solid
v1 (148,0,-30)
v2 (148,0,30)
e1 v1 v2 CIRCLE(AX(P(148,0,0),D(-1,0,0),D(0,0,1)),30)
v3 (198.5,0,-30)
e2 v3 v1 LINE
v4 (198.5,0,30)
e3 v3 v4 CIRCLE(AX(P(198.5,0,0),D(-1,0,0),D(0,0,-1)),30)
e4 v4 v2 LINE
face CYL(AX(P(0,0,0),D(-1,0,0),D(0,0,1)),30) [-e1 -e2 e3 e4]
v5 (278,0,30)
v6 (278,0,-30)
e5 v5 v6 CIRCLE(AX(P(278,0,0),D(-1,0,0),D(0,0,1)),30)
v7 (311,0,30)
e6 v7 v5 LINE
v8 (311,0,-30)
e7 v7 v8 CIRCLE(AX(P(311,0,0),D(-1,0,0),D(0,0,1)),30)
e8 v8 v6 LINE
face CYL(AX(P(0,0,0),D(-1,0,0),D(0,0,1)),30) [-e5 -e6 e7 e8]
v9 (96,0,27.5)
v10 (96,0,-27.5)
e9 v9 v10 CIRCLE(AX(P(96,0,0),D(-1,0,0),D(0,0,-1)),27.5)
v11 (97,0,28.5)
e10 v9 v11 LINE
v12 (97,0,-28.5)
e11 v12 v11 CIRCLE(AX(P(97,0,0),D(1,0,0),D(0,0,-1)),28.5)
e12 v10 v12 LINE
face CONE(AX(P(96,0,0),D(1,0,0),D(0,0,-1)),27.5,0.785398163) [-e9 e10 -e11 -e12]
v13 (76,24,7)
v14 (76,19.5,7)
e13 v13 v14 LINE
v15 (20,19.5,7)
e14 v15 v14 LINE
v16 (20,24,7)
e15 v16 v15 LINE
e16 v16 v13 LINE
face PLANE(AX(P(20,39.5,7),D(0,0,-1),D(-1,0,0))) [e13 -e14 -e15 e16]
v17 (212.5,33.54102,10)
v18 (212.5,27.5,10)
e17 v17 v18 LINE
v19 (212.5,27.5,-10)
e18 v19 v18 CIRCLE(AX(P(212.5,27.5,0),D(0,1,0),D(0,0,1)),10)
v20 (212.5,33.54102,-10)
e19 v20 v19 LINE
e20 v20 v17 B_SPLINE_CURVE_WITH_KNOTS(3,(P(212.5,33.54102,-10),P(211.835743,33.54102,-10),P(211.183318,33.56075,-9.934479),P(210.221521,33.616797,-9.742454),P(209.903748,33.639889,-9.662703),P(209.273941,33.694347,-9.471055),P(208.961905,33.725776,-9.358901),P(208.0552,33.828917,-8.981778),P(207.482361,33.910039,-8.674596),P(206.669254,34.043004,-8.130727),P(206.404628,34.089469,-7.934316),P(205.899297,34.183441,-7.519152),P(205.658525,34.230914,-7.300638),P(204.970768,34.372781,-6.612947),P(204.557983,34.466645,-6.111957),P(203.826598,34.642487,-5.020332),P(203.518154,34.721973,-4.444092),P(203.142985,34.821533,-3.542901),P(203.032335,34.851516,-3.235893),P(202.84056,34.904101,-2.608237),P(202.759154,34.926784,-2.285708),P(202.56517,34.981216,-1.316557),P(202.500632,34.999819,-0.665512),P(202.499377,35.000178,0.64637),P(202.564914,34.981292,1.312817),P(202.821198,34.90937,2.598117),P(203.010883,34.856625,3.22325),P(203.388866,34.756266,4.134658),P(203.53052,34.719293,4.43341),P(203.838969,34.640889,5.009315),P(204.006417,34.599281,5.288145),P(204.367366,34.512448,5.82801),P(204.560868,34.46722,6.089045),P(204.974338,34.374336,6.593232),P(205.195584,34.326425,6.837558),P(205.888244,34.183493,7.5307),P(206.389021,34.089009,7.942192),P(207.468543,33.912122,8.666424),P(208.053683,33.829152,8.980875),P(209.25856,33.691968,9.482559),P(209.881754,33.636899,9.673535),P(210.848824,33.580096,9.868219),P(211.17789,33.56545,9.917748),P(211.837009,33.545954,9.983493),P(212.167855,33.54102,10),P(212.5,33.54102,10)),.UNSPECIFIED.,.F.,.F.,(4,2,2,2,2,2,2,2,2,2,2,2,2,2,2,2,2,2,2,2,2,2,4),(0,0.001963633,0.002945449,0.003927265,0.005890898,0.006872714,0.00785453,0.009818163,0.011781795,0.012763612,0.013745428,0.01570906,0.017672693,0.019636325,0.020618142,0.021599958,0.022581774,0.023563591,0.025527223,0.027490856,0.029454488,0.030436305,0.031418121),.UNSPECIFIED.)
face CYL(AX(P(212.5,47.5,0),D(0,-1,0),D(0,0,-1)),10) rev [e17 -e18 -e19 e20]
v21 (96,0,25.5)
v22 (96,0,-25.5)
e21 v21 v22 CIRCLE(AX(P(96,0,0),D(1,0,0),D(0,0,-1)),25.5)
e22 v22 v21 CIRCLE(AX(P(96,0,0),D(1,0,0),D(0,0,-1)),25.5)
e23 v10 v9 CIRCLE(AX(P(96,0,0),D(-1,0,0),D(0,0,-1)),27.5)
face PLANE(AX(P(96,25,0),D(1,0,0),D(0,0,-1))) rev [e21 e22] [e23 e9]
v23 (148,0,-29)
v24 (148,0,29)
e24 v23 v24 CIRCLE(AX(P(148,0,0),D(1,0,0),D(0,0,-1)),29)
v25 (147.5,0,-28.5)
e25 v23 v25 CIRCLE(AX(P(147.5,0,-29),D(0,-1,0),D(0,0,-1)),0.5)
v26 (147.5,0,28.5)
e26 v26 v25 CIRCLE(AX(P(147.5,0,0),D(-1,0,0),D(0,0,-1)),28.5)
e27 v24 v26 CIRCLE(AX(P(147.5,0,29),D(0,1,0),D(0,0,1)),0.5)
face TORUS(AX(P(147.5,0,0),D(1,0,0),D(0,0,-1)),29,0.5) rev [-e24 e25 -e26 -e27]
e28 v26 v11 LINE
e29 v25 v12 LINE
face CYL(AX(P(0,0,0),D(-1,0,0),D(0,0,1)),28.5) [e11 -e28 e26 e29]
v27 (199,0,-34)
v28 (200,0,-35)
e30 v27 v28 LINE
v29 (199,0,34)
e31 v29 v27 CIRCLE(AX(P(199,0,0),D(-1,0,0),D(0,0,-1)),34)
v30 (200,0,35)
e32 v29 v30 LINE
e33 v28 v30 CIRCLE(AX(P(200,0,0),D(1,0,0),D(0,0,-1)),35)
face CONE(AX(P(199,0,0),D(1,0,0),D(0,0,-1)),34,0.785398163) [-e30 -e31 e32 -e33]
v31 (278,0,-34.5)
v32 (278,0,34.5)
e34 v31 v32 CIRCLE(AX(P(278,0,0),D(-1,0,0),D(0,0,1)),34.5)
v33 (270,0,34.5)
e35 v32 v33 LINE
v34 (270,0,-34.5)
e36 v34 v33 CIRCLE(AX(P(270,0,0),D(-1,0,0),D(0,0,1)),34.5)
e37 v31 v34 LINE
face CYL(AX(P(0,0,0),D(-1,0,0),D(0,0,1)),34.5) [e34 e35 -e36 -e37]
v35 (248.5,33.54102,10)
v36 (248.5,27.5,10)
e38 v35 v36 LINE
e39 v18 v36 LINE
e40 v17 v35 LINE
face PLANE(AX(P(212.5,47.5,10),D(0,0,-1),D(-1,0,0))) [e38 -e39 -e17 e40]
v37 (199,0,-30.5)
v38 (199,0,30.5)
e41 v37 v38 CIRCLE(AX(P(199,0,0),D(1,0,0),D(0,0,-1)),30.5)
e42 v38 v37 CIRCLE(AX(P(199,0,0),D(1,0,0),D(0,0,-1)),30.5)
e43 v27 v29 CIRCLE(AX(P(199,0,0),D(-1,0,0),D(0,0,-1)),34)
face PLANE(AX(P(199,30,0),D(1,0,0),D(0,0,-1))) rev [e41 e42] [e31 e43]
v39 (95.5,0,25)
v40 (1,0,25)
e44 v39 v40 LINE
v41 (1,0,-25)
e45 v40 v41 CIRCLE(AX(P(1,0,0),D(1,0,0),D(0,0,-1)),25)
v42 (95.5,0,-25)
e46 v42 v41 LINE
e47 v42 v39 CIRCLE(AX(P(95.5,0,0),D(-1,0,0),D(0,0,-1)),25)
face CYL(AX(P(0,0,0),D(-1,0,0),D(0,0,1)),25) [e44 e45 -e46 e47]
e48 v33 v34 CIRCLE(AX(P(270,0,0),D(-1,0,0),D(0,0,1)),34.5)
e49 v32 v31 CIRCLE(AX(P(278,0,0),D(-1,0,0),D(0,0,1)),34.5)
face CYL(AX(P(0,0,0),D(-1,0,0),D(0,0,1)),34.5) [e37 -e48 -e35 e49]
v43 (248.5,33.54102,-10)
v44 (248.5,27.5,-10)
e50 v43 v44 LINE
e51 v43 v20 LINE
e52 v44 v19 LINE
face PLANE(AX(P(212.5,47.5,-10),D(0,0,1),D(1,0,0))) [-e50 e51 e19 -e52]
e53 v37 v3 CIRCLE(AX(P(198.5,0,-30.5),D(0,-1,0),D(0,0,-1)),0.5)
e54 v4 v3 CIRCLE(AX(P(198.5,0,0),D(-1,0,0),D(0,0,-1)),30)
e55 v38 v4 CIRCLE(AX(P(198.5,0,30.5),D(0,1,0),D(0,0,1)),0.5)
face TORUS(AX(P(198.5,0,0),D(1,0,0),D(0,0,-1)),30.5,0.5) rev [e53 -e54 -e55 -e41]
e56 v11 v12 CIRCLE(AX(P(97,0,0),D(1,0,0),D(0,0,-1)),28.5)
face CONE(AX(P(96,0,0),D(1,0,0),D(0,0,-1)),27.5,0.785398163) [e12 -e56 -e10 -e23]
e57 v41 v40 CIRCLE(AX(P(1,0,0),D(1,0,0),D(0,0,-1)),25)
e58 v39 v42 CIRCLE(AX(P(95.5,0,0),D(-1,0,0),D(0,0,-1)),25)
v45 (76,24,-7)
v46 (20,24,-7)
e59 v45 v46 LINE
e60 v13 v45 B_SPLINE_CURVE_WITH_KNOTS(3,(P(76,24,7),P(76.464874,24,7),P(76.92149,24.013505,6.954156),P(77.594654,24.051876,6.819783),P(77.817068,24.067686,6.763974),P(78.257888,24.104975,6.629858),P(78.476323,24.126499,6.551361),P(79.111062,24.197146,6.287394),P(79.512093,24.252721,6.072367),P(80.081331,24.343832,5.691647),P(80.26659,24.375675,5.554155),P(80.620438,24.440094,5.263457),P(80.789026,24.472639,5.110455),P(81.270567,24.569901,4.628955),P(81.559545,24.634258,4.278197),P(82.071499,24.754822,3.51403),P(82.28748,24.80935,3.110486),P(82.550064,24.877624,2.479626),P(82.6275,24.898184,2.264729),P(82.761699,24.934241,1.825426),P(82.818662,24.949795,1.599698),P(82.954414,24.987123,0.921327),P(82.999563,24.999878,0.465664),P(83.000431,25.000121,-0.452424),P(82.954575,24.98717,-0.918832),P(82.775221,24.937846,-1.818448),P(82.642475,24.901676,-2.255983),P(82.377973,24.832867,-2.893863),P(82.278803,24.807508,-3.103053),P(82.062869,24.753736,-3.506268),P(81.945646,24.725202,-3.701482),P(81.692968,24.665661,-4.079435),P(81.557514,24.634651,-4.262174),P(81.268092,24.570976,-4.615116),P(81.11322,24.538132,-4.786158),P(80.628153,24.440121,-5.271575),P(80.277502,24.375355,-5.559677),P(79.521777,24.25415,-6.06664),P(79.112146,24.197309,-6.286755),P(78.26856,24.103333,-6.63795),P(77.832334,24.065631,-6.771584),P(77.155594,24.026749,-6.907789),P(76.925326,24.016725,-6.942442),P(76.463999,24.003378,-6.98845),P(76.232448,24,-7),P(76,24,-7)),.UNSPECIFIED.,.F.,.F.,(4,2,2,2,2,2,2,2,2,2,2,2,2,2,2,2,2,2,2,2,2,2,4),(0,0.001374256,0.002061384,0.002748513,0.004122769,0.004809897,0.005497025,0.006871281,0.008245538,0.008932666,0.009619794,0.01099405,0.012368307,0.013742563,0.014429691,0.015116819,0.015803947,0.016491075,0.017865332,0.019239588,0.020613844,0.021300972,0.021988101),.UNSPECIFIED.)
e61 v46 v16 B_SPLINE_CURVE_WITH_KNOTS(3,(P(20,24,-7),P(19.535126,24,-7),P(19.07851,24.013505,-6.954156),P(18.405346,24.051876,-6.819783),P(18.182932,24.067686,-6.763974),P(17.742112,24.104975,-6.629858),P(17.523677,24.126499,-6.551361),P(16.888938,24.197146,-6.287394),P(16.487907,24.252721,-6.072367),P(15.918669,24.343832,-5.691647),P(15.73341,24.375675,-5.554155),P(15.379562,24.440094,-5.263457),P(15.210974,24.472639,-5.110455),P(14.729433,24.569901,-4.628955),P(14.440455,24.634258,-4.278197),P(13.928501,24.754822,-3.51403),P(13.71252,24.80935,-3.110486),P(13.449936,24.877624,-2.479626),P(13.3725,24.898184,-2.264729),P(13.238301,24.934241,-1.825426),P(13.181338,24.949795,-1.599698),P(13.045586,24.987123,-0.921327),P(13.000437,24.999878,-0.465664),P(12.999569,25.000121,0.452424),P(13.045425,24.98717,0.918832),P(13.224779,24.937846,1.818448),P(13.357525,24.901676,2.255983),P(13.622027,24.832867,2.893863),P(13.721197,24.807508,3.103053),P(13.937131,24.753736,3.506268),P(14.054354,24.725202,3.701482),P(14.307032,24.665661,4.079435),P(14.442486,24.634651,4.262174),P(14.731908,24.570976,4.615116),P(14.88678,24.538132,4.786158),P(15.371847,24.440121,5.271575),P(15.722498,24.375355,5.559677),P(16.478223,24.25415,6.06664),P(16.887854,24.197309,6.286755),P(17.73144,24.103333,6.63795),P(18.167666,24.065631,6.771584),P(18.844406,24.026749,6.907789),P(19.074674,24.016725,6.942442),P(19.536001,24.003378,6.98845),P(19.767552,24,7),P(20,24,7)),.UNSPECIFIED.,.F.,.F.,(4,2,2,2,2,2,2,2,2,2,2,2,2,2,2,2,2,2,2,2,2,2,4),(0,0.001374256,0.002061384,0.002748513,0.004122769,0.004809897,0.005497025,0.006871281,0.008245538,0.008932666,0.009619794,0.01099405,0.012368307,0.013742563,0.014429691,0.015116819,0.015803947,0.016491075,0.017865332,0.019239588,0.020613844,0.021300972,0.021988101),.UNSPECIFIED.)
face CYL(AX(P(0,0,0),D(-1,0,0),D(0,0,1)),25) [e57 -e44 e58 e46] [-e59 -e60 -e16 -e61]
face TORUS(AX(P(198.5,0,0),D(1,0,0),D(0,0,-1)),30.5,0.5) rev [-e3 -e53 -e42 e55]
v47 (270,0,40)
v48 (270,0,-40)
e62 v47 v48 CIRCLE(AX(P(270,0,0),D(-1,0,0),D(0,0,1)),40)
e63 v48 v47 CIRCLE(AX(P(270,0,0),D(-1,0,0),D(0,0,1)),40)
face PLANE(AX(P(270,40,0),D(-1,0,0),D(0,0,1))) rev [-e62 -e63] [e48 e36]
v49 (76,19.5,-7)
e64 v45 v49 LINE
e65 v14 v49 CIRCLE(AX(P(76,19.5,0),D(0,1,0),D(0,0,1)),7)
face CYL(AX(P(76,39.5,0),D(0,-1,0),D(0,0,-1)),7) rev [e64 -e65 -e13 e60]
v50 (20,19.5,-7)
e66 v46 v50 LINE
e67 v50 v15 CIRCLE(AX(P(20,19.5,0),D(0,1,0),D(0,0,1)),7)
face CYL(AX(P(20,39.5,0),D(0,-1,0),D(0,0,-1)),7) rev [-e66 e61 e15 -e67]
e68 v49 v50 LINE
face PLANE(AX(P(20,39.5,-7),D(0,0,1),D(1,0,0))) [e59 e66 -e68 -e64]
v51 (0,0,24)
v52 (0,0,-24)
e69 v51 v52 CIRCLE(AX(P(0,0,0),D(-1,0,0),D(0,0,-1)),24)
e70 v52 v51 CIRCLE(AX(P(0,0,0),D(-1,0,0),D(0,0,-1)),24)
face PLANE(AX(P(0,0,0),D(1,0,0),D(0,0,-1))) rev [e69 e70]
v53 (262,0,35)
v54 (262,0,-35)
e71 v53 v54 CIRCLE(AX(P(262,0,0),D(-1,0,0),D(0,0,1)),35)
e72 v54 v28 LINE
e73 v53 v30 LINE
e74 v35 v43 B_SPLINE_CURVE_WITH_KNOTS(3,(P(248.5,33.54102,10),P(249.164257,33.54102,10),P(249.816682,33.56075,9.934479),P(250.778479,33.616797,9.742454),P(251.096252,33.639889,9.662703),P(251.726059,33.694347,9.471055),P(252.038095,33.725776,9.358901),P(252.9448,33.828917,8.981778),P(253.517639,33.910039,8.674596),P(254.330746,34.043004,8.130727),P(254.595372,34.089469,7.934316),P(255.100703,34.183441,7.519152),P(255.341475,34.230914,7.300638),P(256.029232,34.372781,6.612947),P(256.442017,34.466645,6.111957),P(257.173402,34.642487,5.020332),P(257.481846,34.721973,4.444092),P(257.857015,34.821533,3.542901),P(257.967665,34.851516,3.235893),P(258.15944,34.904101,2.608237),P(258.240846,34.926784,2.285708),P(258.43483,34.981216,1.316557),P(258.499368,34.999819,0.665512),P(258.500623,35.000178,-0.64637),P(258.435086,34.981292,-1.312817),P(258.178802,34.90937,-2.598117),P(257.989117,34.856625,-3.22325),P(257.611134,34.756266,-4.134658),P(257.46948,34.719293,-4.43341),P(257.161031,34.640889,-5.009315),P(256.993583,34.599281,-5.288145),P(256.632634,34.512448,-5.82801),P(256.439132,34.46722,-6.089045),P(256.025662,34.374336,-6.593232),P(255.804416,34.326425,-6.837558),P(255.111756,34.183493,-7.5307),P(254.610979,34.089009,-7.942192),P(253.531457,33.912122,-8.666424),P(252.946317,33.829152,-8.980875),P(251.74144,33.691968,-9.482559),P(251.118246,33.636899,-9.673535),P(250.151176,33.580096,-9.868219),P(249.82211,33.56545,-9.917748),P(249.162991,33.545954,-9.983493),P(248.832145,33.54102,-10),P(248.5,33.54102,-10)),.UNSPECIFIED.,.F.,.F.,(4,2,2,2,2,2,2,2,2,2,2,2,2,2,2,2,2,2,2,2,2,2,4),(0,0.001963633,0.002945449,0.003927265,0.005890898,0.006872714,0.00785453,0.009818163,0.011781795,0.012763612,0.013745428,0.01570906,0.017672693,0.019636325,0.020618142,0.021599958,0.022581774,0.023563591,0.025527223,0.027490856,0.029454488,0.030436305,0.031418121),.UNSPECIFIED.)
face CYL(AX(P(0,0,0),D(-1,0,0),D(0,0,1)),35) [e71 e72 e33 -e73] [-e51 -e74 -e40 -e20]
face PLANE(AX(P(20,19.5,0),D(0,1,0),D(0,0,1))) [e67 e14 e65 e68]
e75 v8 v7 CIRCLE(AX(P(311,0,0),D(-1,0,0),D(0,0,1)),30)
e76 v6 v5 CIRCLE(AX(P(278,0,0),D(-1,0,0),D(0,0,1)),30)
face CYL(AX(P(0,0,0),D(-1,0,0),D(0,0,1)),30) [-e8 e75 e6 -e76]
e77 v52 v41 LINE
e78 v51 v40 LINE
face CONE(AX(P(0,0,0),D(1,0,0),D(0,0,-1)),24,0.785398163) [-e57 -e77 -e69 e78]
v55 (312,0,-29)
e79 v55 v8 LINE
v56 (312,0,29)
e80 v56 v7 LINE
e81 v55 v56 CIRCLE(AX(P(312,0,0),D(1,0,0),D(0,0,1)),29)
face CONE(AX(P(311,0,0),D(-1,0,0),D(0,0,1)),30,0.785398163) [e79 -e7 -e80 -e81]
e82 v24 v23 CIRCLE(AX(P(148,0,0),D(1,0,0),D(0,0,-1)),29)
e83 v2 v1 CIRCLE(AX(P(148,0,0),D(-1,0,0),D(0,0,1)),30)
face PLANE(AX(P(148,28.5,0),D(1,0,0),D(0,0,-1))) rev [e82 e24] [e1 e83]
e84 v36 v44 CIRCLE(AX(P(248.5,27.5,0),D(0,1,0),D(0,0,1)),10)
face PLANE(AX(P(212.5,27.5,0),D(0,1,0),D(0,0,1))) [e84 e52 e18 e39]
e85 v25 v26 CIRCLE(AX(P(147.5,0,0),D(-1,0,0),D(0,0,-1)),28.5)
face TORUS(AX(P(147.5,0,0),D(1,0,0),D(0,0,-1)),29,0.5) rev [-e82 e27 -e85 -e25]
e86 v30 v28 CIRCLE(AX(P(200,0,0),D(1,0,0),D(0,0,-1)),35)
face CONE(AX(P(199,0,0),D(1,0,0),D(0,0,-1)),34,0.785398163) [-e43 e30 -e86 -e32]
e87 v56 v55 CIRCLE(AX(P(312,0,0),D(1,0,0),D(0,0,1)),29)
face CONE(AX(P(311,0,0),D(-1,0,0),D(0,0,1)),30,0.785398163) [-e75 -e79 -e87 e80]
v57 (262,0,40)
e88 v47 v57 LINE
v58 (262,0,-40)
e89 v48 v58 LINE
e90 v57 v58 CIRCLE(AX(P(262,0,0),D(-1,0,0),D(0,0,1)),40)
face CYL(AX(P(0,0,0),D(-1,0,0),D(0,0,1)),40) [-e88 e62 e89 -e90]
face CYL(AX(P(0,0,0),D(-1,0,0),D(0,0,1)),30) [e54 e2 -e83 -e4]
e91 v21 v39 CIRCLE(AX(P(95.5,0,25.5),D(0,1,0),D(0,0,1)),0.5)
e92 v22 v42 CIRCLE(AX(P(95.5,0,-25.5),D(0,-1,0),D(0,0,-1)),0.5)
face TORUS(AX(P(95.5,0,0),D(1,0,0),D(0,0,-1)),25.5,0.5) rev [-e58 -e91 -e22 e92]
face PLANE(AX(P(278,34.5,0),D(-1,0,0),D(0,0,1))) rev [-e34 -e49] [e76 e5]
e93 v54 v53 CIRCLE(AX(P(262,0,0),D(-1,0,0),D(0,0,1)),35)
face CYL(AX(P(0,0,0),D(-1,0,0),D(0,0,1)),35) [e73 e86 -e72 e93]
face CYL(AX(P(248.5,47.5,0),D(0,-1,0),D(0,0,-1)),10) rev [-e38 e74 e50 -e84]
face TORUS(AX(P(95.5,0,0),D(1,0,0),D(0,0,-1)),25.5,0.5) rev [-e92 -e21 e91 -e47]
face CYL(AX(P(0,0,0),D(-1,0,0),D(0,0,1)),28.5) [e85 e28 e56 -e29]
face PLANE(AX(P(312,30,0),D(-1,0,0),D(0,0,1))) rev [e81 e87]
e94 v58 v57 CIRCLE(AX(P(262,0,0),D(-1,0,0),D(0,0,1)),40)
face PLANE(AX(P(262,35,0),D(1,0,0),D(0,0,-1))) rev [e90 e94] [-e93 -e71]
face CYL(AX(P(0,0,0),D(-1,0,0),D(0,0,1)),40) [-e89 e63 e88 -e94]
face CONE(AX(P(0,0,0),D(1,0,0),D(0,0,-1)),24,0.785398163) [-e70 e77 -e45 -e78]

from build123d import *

# Parameters (mm, degrees)
CHAMFER1_SIZE      = 1
CHAMFER2_SIZE      = 1
FILLET1_R          = 0.5
CHAMFER3_SIZE      = 1
CHAMFER4_SIZE      = 1
FILLET2_R          = 0.5
CUT_EXTRUDE1_START = 19.5
CUT_EXTRUDE1_DEPTH = 20
CUT_EXTRUDE2_START = 27.5
CUT_EXTRUDE2_DEPTH = 20


with BuildPart() as part:
    # Sketch1 → Revolve3 (revolve)
    with BuildSketch(Plane.XY, mode=Mode.PRIVATE) as revolve3_sk:
        Polygon((0, 0), (0, 25), (96, 25), (96, 28.5), (148, 28.5), (148, 30), (199, 30), (199, 35), (262, 35), (262, 40), (270, 40), (270, 34.5), (278, 34.5), (278, 30), (312, 30), (312, 0), align=None)
    revolve(revolve3_sk.sketch.rotate(Axis((0, 0, 0), (1, 0, 0)), 90), axis=Axis((0, 0, 0), (1, 0, 0)))

    # Chamfer1
    chamfer1_edges = [part.edges().sort_by_distance(p)[0] for p in [
        (0, 0, -25),
    ]]
    chamfer(chamfer1_edges, length=CHAMFER1_SIZE)

    # Chamfer2
    chamfer2_edges = [part.edges().sort_by_distance(p)[0] for p in [
        (312, 0, -30),
    ]]
    chamfer(chamfer2_edges, length=CHAMFER2_SIZE)

    # Fillet1
    fillet1_edges = [part.edges().sort_by_distance(p)[0] for p in [
        (148, 0, -28.5),
        (96, 0, -25),
    ]]
    fillet(fillet1_edges, radius=FILLET1_R)

    # Chamfer3
    chamfer3_edges = [part.edges().sort_by_distance(p)[0] for p in [
        (199, 0, -35),
    ]]
    chamfer(chamfer3_edges, length=CHAMFER3_SIZE)

    # Chamfer4
    chamfer4_edges = [part.edges().sort_by_distance(p)[0] for p in [
        (96, 0, -28.5),
    ]]
    chamfer(chamfer4_edges, length=CHAMFER4_SIZE)

    # Fillet2
    fillet2_edges = [part.edges().sort_by_distance(p)[0] for p in [
        (199, 0, -30),
    ]]
    fillet(fillet2_edges, radius=FILLET2_R)

    # Sketch2 → Cut-Extrude1 (cut)
    with BuildSketch(Plane(origin=(0, 0, 0), x_dir=(1, 0, 0), z_dir=(0, 1, 0)).offset(CUT_EXTRUDE1_START)):
        with BuildLine():
            Line((20, 7), (76, 7))
            ThreePointArc((76, 7), (83, 0), (76, -7))
            Line((76, -7), (20, -7))
            ThreePointArc((20, -7), (13, 0), (20, 7))
        make_face()
    extrude(amount=CUT_EXTRUDE1_DEPTH, mode=Mode.SUBTRACT)

    # Sketch3 → Cut-Extrude2 (cut)
    with BuildSketch(Plane(origin=(0, 0, 0), x_dir=(1, 0, 0), z_dir=(0, 1, 0)).offset(CUT_EXTRUDE2_START)):
        with BuildLine():
            Line((212.5, 10), (248.5, 10))
            ThreePointArc((248.5, 10), (258.5, 0), (248.5, -10))
            Line((248.5, -10), (212.5, -10))
            ThreePointArc((212.5, -10), (202.5, 0), (212.5, 10))
        make_face()
    extrude(amount=CUT_EXTRUDE2_DEPTH, mode=Mode.SUBTRACT)


solid = part.part
